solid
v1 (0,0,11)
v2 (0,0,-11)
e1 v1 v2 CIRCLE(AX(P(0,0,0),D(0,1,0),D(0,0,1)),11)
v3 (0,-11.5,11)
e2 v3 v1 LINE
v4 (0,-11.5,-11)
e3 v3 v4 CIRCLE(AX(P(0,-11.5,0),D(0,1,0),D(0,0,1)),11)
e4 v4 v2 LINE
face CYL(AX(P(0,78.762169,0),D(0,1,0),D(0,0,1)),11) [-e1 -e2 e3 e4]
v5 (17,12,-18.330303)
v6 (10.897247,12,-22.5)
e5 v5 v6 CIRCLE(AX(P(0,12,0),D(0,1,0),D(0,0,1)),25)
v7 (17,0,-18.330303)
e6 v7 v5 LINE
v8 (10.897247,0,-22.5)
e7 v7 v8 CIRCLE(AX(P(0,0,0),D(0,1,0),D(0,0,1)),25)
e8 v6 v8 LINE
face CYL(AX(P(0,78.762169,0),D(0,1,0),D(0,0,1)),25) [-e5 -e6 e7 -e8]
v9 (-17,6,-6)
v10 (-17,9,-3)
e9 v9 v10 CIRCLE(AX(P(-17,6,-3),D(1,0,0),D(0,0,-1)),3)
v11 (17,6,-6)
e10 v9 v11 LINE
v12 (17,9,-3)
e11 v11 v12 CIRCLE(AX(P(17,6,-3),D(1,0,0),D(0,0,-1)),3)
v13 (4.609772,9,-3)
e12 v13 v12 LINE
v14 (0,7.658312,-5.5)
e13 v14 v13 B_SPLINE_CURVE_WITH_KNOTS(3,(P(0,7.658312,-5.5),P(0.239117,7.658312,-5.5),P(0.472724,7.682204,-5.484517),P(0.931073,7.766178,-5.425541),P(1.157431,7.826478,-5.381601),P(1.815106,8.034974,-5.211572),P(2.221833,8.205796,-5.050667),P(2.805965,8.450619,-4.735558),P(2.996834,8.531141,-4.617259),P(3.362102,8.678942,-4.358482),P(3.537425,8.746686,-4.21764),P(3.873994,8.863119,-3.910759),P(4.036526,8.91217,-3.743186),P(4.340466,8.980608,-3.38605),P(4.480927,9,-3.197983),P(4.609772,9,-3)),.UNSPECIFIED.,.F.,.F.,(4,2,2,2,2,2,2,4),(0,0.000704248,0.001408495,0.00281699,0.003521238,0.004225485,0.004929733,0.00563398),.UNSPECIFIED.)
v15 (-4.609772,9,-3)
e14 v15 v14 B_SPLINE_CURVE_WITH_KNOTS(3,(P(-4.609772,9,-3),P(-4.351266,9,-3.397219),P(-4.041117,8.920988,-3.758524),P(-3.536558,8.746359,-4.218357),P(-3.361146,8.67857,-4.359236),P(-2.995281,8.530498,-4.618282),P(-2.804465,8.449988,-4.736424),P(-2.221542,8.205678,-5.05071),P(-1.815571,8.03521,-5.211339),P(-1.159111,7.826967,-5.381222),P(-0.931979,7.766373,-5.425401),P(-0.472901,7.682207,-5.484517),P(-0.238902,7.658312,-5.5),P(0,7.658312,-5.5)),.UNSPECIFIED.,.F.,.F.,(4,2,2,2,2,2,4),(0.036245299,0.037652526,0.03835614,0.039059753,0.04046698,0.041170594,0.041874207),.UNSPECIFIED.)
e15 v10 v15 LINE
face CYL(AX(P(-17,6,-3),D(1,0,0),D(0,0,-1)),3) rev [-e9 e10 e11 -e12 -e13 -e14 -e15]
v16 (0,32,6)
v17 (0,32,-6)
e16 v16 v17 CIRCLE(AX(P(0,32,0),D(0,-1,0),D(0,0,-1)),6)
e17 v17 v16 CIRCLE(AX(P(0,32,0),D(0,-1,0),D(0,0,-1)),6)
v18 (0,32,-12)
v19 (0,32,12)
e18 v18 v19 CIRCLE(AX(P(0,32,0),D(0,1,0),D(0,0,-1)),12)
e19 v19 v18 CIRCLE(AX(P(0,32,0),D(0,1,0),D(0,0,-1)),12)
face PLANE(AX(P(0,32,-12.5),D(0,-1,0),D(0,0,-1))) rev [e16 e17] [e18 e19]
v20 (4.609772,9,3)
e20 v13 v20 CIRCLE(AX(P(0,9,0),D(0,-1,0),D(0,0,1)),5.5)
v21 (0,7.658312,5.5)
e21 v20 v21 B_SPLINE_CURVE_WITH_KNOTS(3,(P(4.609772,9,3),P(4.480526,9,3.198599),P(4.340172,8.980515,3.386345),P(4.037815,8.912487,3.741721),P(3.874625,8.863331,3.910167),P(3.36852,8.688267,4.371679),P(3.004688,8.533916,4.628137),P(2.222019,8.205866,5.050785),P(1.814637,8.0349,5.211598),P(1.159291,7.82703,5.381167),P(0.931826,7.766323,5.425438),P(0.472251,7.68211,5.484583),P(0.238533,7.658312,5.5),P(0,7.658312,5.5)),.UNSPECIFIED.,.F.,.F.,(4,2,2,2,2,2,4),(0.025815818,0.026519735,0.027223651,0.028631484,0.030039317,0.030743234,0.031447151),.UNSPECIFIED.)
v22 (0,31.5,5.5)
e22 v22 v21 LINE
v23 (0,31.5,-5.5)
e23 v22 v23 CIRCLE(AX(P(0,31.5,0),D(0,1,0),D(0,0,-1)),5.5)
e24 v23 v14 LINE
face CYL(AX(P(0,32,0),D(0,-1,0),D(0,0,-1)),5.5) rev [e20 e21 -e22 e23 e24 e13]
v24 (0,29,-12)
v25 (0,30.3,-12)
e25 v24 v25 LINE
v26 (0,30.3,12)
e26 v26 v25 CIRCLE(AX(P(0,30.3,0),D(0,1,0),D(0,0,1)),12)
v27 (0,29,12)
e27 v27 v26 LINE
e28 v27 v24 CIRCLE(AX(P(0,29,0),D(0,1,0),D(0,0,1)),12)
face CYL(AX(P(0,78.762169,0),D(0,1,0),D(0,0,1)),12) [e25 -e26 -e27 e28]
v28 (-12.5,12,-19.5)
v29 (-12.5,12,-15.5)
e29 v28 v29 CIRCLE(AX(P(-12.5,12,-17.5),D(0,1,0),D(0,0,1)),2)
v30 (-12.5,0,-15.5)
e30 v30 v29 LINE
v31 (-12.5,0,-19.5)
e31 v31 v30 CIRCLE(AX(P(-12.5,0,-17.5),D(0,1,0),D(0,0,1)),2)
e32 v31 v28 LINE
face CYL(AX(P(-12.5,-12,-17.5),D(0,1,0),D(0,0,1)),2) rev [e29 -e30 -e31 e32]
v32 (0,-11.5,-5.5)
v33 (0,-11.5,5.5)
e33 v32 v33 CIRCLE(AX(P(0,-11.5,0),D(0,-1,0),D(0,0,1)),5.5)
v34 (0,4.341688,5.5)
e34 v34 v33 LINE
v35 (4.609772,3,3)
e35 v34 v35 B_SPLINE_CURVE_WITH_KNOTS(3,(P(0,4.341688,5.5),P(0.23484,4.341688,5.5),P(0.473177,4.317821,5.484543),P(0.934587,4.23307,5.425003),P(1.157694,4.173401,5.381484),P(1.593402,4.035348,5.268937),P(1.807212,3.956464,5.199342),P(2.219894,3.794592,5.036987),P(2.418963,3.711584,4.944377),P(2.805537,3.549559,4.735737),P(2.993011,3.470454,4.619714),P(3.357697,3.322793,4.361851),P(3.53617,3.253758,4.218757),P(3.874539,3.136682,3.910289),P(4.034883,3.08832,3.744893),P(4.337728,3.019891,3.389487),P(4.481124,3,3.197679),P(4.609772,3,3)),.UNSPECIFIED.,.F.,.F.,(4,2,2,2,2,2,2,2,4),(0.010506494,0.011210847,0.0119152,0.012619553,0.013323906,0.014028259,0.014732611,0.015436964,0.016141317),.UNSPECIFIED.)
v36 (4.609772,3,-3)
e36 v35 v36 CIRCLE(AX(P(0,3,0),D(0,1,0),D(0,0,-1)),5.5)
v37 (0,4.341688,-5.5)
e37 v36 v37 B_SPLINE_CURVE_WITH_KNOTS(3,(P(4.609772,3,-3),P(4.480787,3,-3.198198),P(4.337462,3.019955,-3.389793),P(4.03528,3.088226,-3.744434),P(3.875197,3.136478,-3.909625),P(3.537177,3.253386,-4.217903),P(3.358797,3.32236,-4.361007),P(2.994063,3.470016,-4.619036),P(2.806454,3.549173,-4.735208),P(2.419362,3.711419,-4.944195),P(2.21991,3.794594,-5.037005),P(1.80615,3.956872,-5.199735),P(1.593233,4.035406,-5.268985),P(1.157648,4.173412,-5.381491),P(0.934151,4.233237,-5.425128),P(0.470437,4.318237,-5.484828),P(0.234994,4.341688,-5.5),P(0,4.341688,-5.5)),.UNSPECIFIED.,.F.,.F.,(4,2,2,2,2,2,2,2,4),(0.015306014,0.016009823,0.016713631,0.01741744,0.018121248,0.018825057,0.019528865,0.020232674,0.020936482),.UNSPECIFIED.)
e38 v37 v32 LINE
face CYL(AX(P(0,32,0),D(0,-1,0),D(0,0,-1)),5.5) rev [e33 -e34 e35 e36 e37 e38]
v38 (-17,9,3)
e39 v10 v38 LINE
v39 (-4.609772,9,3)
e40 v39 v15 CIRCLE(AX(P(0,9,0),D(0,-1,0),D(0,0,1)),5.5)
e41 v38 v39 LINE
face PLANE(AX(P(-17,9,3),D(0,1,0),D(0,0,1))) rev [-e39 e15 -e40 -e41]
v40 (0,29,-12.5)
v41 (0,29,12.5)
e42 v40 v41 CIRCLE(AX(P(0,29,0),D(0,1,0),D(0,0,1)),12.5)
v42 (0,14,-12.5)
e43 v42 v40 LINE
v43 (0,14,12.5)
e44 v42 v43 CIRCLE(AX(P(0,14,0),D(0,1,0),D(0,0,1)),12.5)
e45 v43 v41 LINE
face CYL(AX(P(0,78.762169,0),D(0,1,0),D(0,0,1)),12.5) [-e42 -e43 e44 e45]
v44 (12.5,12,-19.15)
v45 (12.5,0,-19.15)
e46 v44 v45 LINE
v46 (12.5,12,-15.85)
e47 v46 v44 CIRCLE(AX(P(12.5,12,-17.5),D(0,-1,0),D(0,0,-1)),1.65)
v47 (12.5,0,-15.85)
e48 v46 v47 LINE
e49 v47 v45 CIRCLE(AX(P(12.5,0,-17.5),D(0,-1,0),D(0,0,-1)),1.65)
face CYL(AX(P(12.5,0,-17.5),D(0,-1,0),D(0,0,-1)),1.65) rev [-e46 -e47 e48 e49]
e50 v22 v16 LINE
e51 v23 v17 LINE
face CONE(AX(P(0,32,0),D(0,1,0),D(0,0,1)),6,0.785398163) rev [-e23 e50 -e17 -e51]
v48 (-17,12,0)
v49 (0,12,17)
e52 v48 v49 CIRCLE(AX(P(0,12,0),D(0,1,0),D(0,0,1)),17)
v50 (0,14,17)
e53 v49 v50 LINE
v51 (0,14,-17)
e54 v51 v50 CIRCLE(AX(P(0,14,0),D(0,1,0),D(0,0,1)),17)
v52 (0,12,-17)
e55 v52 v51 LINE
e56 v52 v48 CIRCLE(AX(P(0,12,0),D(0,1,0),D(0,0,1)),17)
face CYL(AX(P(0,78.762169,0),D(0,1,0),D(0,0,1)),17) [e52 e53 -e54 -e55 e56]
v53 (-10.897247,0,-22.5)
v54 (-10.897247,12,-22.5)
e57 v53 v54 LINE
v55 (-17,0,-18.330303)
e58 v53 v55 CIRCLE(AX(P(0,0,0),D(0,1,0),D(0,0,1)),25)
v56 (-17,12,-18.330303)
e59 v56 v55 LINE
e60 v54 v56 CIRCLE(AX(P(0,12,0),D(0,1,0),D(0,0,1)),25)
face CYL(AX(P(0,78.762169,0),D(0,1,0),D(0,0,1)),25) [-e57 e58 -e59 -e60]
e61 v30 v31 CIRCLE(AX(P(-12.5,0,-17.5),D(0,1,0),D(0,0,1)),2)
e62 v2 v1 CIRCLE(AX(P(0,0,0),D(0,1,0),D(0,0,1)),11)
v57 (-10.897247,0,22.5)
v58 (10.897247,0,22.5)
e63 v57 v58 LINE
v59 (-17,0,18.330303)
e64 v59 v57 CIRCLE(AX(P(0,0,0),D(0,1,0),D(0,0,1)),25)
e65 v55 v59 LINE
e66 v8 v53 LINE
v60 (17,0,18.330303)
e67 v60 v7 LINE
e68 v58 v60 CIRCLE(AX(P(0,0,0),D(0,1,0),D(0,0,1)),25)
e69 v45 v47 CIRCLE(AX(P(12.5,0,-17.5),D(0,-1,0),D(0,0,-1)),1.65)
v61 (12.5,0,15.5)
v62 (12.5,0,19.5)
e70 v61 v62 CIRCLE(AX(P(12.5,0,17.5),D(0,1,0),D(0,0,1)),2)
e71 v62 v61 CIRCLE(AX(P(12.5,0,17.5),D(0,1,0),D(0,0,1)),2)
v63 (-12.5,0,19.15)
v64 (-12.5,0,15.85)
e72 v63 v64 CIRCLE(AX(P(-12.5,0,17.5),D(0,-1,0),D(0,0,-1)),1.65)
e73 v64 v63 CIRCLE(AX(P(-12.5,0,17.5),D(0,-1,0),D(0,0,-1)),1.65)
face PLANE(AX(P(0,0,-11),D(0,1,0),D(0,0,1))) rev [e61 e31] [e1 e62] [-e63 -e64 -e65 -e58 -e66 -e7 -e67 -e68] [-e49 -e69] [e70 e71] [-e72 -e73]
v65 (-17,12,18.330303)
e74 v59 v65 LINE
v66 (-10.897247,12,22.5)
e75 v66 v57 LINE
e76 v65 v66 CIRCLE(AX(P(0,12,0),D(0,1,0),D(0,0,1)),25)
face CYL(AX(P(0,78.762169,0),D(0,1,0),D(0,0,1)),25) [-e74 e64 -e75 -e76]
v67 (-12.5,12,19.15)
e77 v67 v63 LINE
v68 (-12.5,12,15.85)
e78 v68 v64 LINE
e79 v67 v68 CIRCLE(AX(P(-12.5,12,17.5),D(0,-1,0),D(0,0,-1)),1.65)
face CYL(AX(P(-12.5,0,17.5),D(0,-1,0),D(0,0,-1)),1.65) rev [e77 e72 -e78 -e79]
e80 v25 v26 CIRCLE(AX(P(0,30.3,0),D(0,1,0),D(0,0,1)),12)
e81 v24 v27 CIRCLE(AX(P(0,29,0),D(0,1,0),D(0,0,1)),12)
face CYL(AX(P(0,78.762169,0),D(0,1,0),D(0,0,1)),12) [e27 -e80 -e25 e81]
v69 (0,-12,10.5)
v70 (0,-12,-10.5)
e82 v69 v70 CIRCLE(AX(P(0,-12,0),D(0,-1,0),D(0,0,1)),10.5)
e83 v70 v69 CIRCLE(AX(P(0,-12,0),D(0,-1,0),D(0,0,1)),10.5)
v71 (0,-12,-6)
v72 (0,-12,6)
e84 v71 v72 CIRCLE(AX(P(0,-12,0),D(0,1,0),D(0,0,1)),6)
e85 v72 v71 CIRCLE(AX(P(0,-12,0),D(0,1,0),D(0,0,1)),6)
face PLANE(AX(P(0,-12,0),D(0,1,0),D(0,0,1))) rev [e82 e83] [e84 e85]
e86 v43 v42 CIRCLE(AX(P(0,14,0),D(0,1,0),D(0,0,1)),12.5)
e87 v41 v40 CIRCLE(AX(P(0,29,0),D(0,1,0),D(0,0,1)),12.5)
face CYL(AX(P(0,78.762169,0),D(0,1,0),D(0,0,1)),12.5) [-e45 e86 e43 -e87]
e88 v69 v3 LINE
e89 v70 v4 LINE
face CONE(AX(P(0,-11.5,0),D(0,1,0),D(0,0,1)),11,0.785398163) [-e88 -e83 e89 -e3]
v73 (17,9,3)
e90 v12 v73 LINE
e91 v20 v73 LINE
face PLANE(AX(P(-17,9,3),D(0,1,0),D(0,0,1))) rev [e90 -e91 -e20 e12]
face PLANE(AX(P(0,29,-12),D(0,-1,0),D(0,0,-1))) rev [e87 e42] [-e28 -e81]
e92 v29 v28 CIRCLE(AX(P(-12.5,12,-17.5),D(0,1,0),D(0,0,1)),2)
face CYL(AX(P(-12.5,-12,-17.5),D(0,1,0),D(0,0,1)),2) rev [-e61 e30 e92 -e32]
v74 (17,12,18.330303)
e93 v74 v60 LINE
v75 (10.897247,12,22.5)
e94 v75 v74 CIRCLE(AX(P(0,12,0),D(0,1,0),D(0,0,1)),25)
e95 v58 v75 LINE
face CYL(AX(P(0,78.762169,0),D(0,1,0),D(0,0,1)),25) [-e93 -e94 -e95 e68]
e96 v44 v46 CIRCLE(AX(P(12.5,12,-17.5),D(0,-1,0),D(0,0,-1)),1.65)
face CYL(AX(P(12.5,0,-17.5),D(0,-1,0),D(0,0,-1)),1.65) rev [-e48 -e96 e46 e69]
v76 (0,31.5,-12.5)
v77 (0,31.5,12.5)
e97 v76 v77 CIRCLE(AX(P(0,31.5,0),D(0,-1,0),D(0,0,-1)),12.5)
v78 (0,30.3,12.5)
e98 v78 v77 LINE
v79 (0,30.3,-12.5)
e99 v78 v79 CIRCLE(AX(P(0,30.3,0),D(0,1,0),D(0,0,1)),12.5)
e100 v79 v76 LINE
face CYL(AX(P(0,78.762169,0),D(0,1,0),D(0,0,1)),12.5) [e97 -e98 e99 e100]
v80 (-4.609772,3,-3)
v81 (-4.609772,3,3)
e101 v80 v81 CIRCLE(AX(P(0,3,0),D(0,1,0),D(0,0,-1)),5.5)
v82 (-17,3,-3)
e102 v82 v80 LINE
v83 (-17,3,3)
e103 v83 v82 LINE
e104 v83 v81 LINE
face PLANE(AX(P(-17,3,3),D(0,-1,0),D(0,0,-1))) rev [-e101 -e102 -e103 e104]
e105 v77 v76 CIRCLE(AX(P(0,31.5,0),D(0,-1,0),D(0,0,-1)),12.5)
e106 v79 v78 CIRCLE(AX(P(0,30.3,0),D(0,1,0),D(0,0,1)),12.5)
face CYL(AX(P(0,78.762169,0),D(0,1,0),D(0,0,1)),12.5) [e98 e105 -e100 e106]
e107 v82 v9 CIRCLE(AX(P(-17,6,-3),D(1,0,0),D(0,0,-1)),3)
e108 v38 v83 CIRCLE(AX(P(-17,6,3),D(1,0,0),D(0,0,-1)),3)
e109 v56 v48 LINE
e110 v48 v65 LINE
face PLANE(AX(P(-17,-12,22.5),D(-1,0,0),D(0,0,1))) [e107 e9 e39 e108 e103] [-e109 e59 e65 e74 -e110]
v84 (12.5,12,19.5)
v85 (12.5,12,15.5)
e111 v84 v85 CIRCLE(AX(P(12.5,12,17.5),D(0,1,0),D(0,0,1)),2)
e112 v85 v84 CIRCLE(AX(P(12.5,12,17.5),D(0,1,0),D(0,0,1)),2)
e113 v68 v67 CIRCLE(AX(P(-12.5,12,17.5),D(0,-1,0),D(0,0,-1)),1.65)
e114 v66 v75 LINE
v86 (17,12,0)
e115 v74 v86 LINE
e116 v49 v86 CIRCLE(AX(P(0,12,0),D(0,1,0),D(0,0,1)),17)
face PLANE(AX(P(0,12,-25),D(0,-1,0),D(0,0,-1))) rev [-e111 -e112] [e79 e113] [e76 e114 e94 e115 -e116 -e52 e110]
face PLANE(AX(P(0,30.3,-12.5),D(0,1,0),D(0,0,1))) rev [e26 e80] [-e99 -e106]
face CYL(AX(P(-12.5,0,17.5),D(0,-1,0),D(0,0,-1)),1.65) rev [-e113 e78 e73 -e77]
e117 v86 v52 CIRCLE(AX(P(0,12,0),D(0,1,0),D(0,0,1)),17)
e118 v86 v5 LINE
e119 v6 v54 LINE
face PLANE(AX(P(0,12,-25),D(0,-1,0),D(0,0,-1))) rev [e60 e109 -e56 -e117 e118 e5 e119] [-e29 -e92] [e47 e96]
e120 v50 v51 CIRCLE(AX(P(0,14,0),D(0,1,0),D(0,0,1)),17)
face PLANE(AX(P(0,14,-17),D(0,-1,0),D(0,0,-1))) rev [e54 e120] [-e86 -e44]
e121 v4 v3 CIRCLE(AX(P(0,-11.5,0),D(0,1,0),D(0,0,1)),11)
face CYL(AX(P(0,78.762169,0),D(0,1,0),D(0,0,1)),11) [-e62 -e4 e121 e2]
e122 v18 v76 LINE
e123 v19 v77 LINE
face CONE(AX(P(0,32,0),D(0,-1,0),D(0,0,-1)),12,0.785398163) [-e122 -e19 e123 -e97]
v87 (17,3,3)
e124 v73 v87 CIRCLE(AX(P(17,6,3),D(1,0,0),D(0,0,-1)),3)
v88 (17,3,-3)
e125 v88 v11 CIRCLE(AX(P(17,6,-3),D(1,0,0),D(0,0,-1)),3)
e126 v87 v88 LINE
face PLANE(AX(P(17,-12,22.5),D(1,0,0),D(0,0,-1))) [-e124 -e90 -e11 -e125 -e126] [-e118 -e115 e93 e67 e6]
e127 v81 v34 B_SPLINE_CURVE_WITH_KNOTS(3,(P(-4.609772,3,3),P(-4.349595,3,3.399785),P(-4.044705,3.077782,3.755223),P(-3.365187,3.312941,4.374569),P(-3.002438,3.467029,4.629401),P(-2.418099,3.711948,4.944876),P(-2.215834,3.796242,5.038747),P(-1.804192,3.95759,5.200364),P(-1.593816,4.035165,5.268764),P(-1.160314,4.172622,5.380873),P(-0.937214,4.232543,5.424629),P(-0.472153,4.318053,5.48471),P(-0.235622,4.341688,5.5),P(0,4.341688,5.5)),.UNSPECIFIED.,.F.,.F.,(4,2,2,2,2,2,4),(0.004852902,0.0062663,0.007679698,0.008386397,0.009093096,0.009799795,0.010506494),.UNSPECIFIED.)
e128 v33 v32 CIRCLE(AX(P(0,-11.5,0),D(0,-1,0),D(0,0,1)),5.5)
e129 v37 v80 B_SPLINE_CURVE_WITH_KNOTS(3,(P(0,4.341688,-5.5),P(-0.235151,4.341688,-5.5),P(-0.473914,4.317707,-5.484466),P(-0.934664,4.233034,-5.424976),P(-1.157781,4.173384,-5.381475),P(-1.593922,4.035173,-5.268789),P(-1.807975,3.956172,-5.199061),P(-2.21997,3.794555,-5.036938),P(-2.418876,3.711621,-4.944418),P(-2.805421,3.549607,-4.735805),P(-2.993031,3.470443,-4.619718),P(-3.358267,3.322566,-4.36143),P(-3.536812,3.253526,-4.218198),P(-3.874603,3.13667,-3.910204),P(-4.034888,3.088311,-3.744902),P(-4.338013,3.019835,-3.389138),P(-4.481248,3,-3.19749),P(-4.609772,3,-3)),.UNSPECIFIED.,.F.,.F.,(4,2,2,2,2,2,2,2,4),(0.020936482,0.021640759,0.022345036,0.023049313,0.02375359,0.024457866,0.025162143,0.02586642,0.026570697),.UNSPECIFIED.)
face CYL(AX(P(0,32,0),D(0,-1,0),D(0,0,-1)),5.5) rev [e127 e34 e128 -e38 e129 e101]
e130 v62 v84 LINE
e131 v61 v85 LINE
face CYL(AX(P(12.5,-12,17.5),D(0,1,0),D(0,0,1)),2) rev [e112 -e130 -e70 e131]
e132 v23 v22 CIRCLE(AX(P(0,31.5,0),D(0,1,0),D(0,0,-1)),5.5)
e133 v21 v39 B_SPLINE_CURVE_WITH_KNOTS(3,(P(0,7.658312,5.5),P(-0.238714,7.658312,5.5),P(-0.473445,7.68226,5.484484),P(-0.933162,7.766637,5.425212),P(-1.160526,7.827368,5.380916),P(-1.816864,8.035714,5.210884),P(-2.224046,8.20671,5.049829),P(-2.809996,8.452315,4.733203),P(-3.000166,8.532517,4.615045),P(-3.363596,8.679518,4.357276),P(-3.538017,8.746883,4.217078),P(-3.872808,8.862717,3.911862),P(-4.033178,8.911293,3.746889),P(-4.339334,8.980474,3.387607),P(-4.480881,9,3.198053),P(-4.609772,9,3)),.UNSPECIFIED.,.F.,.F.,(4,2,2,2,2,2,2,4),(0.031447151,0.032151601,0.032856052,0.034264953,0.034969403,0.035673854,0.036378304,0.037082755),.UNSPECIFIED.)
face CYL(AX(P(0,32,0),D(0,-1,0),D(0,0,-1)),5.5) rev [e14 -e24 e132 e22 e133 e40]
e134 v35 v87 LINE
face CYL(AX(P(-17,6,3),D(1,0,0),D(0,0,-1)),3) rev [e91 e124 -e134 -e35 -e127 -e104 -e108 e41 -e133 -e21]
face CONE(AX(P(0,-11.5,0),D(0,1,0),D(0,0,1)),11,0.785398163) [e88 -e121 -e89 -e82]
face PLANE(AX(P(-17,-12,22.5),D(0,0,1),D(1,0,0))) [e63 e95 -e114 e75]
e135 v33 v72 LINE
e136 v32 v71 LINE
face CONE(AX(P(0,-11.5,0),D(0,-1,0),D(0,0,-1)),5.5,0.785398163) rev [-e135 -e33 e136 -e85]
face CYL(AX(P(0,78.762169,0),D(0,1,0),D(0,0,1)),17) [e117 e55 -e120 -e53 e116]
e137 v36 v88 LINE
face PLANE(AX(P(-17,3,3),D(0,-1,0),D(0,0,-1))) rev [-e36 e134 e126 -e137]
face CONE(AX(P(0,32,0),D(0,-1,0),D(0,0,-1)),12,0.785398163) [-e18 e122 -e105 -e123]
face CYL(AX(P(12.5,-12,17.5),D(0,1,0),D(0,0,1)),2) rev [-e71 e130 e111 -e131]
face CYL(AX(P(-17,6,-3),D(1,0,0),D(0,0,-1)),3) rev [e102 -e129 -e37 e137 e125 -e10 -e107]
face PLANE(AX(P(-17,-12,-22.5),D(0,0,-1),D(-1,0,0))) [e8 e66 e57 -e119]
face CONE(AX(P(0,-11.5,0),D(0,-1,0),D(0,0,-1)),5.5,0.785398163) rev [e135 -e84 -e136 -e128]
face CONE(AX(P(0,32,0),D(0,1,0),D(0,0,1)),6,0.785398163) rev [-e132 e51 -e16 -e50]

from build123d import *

# Parameters (mm, degrees)
SKETCH2_OUTSIDE_W   = 68.656
SKETCH2_OUTSIDE_H   = 68.656
SKETCH2_OUTSIDE_W_2 = 34
SKETCH2_OUTSIDE_H_2 = 45
CUT_EXTRUDE1_DEPTH  = 43.731721238
SKETCH3_R           = 5.5
CUT_EXTRUDE2_DEPTH  = 53.261362401
M4_TAPPED_HOLE1_D   = 3.3
SKETCH14_R          = 2
CUT_EXTRUDE5_DEPTH  = 38.030392923
CHAMFER1_SIZE       = 0.5
CHAMFER2_SIZE       = 0.5
CUT_EXTRUDE6_DEPTH  = 52.829045911


with BuildPart() as part:
    # Sketch1 → Revolve1 (revolve)
    with BuildSketch(Plane(origin=(0, 0, 0), x_dir=(0, 0, -1), z_dir=(1, 0, 0)), mode=Mode.PRIVATE) as revolve1_sk:
        Polygon((0, -12), (11, -12), (11, 0), (25, 0), (25, 12), (17, 12), (17, 14), (12.5, 14), (12.5, 29), (12, 29), (12, 30.3), (12.5, 30.3), (12.5, 32), (0, 32), align=None)
    revolve(revolve1_sk.sketch.rotate(Axis((0, 78.762169225, 0), (0, -1, 0)), 180), axis=Axis((0, 78.762169225, 0), (0, -1, 0)))

    # Sketch2 outside → Cut-Extrude1 (cut, through all)
    with BuildSketch(Plane(origin=(0, 12, 0), x_dir=(1, 0, 0), z_dir=(0, 1, 0))):
        Rectangle(SKETCH2_OUTSIDE_W, SKETCH2_OUTSIDE_H)
        Rectangle(SKETCH2_OUTSIDE_W_2, SKETCH2_OUTSIDE_H_2, mode=Mode.SUBTRACT)
    extrude(amount=-CUT_EXTRUDE1_DEPTH, mode=Mode.SUBTRACT)

    # Sketch3 → Cut-Extrude2 (cut, through all)
    with BuildSketch(Plane.XZ.offset(12)):
        with Locations(Location((0, 0, 0), (0, 0, 270))):
            Circle(SKETCH3_R)
    extrude(amount=-CUT_EXTRUDE2_DEPTH, mode=Mode.SUBTRACT)

    # M4 Tapped Hole1 (through all)
    with Locations(Plane(origin=(0, 0, 0), x_dir=(-1, 0, 0), z_dir=(0, -1, 0))):
        with Locations((-12.5, 17.5), (12.5, -17.5)):
            Hole(M4_TAPPED_HOLE1_D / 2)

    # Sketch14 → Cut-Extrude5 (cut, through all)
    with BuildSketch(Plane(origin=(0, 12, 0), x_dir=(1, 0, 0), z_dir=(0, 1, 0))):
        with Locations(Location((12.5, -17.5, 0), (0, 0, 270))):
            Circle(SKETCH14_R)
        with Locations(Location((-12.5, 17.5, 0), (0, 0, 270))):
            Circle(SKETCH14_R)
    extrude(amount=-CUT_EXTRUDE5_DEPTH, mode=Mode.SUBTRACT)

    # Chamfer1
    chamfer1_edges = [part.edges().sort_by_distance(p)[0] for p in [
        (0, -12, -11),
        (0, 32, -12.5),
    ]]
    chamfer(chamfer1_edges, length=CHAMFER1_SIZE)

    # Chamfer2
    chamfer2_edges = [part.edges().sort_by_distance(p)[0] for p in [
        (0, 32, 5.5),
        (0, -12, 5.5),
    ]]
    chamfer(chamfer2_edges, length=CHAMFER2_SIZE)

    # Sketch15 → Cut-Extrude6 (cut, through all)
    with BuildSketch(Plane(origin=(17, 0, 0), x_dir=(0, 0, -1), z_dir=(1, 0, 0))):
        with BuildLine():
            Line((-3, 9), (3, 9))
            ThreePointArc((3, 9), (6, 6), (3, 3))
            Line((3, 3), (-3, 3))
            ThreePointArc((-3, 3), (-6, 6), (-3, 9))
        make_face()
    extrude(amount=-CUT_EXTRUDE6_DEPTH, mode=Mode.SUBTRACT)


solid = part.part
